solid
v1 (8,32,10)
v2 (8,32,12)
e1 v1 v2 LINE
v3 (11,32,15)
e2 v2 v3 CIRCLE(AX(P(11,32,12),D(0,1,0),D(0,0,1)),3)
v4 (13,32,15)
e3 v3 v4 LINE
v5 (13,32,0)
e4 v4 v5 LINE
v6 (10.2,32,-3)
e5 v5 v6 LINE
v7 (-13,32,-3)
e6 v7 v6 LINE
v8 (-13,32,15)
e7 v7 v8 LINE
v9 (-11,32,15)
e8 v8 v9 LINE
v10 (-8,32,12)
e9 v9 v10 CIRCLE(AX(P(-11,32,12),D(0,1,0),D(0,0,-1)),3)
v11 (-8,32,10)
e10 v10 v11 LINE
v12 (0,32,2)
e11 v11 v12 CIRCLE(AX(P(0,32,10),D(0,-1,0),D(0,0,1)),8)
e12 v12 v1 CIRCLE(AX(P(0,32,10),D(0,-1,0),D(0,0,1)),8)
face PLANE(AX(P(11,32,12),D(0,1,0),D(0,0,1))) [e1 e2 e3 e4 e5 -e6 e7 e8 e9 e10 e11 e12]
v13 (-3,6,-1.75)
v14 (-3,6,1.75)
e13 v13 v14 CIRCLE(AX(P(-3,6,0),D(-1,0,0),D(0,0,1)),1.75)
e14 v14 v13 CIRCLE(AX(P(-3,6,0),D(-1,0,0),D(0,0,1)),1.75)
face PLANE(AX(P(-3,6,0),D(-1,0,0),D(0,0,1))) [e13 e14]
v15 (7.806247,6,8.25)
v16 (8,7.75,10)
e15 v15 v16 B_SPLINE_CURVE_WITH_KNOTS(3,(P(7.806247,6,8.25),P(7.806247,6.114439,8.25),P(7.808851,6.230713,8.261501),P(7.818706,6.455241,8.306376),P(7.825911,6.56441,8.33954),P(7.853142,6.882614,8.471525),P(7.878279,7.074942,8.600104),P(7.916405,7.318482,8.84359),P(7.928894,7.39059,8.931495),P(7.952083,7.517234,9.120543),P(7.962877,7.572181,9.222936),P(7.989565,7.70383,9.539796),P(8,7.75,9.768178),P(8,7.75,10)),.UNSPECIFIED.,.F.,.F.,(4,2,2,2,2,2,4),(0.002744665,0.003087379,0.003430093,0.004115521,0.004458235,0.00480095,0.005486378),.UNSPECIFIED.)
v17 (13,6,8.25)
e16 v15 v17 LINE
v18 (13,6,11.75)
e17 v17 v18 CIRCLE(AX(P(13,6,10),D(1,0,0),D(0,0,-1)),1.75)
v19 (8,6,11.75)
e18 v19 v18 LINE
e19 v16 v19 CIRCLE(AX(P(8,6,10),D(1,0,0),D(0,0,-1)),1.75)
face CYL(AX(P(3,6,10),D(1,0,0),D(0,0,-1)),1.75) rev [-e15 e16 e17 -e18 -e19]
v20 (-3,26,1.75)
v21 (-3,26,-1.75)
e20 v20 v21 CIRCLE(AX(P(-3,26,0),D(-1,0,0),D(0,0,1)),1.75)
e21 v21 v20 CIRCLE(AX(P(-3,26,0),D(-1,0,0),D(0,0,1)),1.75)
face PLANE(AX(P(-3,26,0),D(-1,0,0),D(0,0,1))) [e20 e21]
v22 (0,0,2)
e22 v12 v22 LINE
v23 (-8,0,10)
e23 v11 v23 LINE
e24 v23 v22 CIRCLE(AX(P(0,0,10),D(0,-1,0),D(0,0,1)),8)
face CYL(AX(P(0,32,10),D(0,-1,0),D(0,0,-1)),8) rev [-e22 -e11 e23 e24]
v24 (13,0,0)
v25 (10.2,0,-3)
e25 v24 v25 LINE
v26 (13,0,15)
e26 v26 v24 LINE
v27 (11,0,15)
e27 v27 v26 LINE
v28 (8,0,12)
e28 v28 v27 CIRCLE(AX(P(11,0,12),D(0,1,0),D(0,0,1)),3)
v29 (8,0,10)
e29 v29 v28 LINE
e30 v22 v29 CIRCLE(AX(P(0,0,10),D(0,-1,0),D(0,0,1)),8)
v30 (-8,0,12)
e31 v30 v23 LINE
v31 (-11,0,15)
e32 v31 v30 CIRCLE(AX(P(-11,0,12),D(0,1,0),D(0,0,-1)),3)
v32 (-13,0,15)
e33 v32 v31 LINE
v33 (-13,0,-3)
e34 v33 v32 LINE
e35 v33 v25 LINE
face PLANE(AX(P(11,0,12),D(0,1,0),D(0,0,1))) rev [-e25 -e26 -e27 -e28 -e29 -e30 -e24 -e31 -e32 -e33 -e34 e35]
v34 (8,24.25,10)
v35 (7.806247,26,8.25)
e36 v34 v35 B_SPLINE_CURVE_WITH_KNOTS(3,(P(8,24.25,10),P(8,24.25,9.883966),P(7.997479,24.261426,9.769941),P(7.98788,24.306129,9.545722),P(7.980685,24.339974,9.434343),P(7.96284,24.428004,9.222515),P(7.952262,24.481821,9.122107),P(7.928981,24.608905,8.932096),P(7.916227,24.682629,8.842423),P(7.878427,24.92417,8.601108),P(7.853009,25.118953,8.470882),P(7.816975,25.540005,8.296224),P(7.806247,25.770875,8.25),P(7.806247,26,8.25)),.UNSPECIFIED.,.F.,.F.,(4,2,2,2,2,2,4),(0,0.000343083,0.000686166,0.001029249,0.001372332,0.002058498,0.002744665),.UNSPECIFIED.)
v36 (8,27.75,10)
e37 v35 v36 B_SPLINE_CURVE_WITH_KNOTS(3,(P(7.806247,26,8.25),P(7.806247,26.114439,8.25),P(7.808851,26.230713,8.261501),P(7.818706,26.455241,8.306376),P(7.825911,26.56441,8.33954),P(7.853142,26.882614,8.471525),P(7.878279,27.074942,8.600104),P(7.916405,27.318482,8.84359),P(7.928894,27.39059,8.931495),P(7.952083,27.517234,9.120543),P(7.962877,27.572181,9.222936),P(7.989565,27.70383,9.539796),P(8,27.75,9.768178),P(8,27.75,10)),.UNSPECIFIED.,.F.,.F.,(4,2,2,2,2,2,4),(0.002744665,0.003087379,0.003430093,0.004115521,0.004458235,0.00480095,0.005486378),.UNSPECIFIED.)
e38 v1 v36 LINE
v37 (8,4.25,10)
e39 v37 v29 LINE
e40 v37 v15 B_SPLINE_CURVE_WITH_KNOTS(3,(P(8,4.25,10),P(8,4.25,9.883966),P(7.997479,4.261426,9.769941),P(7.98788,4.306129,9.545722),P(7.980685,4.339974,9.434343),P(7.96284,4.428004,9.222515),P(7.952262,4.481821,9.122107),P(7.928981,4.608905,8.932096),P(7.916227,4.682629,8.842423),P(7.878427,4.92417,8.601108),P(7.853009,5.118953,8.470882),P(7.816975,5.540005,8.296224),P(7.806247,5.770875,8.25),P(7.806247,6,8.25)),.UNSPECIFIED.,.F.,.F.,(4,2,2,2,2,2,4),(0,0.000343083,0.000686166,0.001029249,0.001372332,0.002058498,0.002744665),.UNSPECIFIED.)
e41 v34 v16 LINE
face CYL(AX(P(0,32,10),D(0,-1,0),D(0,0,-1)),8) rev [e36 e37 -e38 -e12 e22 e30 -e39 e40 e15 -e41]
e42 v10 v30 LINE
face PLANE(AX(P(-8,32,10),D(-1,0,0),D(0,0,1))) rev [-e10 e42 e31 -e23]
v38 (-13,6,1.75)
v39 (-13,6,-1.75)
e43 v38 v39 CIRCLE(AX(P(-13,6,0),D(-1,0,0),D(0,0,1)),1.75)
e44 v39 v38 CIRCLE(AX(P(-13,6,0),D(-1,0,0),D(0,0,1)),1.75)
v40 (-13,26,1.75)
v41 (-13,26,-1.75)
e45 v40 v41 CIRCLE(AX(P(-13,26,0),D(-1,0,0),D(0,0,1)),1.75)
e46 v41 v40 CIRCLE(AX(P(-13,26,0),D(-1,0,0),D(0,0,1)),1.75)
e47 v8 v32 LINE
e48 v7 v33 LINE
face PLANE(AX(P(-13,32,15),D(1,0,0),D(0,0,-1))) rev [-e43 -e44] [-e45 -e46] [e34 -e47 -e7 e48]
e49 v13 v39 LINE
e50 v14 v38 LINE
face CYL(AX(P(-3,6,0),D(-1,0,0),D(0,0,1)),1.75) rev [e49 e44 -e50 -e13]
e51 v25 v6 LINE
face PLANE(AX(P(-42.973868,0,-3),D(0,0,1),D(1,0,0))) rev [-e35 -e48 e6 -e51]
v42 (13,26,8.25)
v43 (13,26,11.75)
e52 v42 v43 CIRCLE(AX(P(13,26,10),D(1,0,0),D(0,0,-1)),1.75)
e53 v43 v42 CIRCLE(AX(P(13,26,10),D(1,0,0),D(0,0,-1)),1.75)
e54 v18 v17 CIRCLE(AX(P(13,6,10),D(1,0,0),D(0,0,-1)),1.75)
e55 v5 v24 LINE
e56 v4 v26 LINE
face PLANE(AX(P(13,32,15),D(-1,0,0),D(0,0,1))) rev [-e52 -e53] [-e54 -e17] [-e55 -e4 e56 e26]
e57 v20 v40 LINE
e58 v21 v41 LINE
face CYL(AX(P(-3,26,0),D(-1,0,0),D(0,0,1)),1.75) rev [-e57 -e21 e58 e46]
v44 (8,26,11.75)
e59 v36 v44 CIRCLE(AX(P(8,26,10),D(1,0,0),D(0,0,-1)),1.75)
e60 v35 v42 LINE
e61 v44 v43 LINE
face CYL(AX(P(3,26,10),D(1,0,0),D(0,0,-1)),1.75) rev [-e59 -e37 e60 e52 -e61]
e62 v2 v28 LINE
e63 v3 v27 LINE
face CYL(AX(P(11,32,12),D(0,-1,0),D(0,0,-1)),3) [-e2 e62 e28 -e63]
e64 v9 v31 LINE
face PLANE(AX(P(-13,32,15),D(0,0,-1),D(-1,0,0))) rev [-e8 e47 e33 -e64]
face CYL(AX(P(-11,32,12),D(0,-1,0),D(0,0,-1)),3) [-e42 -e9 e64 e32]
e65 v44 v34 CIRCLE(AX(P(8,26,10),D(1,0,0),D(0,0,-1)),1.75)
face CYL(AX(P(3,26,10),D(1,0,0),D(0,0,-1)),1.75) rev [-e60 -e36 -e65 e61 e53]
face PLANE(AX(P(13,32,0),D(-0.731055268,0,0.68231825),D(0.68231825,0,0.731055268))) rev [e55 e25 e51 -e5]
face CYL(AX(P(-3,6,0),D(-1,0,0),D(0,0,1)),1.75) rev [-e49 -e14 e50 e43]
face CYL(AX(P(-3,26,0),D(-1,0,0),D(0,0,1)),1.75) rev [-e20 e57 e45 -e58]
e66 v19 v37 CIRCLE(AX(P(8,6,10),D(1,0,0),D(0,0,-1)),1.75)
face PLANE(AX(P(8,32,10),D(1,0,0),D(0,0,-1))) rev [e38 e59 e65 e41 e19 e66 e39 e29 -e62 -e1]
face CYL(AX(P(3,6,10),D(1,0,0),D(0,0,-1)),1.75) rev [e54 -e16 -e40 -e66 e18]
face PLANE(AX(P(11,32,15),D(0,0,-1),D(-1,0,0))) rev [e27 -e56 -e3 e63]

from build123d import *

# Parameters (mm, degrees)
BOSS_EXTRUDE1_DEPTH = 32
SKETCH2_R           = 1.75
CUT_EXTRUDE1_DEPTH  = 10
SKETCH3_W           = 67.397349656
SKETCH3_H           = 25.662976956
CUT_EXTRUDE2_DEPTH  = 38.656340887
SKETCH4_R           = 1.75
CUT_EXTRUDE3_DEPTH  = 10


with BuildPart() as part:
    # Sketch1 → Boss-Extrude1 (new body)
    with BuildSketch(Plane(origin=(0, 0, 0), x_dir=(1, 0, 0), z_dir=(0, 1, 0))):
        with BuildLine():
            Line((-8, -10), (-8, -12))
            ThreePointArc((-8, -12), (-8.878679656, -14.121320344), (-11, -15))
            Line((-11, -15), (-13, -15))
            Line((-13, -15), (-13, 15))
            Line((-13, 15), (-1, 15))
            Line((-1, 15), (13, 0))
            Line((13, 0), (13, -15))
            Line((13, -15), (11, -15))
            ThreePointArc((11, -15), (8.878679656, -14.121320344), (8, -12))
            Line((8, -12), (8, -10))
            ThreePointArc((8, -10), (0, -2), (-8, -10))
        make_face()
    extrude(amount=BOSS_EXTRUDE1_DEPTH)

    # Sketch2 → Cut-Extrude1 (cut)
    with BuildSketch(Plane(origin=(13, 0, 0), x_dir=(0, 0, -1), z_dir=(1, 0, 0))):
        with Locations((-10, 26)):
            Circle(SKETCH2_R)
        with Locations((-10, 6)):
            Circle(SKETCH2_R)
    extrude(amount=-CUT_EXTRUDE1_DEPTH, mode=Mode.SUBTRACT)

    # Sketch3 → Cut-Extrude2 (cut, through all)
    with BuildSketch(Plane(origin=(0, 32, 0), x_dir=(1, 0, 0), z_dir=(0, 1, 0))):
        with Locations((-9.275193266, 15.831488478)):
            Rectangle(SKETCH3_W, SKETCH3_H)
    extrude(amount=-CUT_EXTRUDE2_DEPTH, mode=Mode.SUBTRACT)

    # Sketch4 → Cut-Extrude3 (cut)
    with BuildSketch(Plane.ZY.offset(13)):
        with Locations((0, 6)):
            Circle(SKETCH4_R)
        with Locations((0, 26)):
            Circle(SKETCH4_R)
    extrude(amount=-CUT_EXTRUDE3_DEPTH, mode=Mode.SUBTRACT)


solid = part.part
